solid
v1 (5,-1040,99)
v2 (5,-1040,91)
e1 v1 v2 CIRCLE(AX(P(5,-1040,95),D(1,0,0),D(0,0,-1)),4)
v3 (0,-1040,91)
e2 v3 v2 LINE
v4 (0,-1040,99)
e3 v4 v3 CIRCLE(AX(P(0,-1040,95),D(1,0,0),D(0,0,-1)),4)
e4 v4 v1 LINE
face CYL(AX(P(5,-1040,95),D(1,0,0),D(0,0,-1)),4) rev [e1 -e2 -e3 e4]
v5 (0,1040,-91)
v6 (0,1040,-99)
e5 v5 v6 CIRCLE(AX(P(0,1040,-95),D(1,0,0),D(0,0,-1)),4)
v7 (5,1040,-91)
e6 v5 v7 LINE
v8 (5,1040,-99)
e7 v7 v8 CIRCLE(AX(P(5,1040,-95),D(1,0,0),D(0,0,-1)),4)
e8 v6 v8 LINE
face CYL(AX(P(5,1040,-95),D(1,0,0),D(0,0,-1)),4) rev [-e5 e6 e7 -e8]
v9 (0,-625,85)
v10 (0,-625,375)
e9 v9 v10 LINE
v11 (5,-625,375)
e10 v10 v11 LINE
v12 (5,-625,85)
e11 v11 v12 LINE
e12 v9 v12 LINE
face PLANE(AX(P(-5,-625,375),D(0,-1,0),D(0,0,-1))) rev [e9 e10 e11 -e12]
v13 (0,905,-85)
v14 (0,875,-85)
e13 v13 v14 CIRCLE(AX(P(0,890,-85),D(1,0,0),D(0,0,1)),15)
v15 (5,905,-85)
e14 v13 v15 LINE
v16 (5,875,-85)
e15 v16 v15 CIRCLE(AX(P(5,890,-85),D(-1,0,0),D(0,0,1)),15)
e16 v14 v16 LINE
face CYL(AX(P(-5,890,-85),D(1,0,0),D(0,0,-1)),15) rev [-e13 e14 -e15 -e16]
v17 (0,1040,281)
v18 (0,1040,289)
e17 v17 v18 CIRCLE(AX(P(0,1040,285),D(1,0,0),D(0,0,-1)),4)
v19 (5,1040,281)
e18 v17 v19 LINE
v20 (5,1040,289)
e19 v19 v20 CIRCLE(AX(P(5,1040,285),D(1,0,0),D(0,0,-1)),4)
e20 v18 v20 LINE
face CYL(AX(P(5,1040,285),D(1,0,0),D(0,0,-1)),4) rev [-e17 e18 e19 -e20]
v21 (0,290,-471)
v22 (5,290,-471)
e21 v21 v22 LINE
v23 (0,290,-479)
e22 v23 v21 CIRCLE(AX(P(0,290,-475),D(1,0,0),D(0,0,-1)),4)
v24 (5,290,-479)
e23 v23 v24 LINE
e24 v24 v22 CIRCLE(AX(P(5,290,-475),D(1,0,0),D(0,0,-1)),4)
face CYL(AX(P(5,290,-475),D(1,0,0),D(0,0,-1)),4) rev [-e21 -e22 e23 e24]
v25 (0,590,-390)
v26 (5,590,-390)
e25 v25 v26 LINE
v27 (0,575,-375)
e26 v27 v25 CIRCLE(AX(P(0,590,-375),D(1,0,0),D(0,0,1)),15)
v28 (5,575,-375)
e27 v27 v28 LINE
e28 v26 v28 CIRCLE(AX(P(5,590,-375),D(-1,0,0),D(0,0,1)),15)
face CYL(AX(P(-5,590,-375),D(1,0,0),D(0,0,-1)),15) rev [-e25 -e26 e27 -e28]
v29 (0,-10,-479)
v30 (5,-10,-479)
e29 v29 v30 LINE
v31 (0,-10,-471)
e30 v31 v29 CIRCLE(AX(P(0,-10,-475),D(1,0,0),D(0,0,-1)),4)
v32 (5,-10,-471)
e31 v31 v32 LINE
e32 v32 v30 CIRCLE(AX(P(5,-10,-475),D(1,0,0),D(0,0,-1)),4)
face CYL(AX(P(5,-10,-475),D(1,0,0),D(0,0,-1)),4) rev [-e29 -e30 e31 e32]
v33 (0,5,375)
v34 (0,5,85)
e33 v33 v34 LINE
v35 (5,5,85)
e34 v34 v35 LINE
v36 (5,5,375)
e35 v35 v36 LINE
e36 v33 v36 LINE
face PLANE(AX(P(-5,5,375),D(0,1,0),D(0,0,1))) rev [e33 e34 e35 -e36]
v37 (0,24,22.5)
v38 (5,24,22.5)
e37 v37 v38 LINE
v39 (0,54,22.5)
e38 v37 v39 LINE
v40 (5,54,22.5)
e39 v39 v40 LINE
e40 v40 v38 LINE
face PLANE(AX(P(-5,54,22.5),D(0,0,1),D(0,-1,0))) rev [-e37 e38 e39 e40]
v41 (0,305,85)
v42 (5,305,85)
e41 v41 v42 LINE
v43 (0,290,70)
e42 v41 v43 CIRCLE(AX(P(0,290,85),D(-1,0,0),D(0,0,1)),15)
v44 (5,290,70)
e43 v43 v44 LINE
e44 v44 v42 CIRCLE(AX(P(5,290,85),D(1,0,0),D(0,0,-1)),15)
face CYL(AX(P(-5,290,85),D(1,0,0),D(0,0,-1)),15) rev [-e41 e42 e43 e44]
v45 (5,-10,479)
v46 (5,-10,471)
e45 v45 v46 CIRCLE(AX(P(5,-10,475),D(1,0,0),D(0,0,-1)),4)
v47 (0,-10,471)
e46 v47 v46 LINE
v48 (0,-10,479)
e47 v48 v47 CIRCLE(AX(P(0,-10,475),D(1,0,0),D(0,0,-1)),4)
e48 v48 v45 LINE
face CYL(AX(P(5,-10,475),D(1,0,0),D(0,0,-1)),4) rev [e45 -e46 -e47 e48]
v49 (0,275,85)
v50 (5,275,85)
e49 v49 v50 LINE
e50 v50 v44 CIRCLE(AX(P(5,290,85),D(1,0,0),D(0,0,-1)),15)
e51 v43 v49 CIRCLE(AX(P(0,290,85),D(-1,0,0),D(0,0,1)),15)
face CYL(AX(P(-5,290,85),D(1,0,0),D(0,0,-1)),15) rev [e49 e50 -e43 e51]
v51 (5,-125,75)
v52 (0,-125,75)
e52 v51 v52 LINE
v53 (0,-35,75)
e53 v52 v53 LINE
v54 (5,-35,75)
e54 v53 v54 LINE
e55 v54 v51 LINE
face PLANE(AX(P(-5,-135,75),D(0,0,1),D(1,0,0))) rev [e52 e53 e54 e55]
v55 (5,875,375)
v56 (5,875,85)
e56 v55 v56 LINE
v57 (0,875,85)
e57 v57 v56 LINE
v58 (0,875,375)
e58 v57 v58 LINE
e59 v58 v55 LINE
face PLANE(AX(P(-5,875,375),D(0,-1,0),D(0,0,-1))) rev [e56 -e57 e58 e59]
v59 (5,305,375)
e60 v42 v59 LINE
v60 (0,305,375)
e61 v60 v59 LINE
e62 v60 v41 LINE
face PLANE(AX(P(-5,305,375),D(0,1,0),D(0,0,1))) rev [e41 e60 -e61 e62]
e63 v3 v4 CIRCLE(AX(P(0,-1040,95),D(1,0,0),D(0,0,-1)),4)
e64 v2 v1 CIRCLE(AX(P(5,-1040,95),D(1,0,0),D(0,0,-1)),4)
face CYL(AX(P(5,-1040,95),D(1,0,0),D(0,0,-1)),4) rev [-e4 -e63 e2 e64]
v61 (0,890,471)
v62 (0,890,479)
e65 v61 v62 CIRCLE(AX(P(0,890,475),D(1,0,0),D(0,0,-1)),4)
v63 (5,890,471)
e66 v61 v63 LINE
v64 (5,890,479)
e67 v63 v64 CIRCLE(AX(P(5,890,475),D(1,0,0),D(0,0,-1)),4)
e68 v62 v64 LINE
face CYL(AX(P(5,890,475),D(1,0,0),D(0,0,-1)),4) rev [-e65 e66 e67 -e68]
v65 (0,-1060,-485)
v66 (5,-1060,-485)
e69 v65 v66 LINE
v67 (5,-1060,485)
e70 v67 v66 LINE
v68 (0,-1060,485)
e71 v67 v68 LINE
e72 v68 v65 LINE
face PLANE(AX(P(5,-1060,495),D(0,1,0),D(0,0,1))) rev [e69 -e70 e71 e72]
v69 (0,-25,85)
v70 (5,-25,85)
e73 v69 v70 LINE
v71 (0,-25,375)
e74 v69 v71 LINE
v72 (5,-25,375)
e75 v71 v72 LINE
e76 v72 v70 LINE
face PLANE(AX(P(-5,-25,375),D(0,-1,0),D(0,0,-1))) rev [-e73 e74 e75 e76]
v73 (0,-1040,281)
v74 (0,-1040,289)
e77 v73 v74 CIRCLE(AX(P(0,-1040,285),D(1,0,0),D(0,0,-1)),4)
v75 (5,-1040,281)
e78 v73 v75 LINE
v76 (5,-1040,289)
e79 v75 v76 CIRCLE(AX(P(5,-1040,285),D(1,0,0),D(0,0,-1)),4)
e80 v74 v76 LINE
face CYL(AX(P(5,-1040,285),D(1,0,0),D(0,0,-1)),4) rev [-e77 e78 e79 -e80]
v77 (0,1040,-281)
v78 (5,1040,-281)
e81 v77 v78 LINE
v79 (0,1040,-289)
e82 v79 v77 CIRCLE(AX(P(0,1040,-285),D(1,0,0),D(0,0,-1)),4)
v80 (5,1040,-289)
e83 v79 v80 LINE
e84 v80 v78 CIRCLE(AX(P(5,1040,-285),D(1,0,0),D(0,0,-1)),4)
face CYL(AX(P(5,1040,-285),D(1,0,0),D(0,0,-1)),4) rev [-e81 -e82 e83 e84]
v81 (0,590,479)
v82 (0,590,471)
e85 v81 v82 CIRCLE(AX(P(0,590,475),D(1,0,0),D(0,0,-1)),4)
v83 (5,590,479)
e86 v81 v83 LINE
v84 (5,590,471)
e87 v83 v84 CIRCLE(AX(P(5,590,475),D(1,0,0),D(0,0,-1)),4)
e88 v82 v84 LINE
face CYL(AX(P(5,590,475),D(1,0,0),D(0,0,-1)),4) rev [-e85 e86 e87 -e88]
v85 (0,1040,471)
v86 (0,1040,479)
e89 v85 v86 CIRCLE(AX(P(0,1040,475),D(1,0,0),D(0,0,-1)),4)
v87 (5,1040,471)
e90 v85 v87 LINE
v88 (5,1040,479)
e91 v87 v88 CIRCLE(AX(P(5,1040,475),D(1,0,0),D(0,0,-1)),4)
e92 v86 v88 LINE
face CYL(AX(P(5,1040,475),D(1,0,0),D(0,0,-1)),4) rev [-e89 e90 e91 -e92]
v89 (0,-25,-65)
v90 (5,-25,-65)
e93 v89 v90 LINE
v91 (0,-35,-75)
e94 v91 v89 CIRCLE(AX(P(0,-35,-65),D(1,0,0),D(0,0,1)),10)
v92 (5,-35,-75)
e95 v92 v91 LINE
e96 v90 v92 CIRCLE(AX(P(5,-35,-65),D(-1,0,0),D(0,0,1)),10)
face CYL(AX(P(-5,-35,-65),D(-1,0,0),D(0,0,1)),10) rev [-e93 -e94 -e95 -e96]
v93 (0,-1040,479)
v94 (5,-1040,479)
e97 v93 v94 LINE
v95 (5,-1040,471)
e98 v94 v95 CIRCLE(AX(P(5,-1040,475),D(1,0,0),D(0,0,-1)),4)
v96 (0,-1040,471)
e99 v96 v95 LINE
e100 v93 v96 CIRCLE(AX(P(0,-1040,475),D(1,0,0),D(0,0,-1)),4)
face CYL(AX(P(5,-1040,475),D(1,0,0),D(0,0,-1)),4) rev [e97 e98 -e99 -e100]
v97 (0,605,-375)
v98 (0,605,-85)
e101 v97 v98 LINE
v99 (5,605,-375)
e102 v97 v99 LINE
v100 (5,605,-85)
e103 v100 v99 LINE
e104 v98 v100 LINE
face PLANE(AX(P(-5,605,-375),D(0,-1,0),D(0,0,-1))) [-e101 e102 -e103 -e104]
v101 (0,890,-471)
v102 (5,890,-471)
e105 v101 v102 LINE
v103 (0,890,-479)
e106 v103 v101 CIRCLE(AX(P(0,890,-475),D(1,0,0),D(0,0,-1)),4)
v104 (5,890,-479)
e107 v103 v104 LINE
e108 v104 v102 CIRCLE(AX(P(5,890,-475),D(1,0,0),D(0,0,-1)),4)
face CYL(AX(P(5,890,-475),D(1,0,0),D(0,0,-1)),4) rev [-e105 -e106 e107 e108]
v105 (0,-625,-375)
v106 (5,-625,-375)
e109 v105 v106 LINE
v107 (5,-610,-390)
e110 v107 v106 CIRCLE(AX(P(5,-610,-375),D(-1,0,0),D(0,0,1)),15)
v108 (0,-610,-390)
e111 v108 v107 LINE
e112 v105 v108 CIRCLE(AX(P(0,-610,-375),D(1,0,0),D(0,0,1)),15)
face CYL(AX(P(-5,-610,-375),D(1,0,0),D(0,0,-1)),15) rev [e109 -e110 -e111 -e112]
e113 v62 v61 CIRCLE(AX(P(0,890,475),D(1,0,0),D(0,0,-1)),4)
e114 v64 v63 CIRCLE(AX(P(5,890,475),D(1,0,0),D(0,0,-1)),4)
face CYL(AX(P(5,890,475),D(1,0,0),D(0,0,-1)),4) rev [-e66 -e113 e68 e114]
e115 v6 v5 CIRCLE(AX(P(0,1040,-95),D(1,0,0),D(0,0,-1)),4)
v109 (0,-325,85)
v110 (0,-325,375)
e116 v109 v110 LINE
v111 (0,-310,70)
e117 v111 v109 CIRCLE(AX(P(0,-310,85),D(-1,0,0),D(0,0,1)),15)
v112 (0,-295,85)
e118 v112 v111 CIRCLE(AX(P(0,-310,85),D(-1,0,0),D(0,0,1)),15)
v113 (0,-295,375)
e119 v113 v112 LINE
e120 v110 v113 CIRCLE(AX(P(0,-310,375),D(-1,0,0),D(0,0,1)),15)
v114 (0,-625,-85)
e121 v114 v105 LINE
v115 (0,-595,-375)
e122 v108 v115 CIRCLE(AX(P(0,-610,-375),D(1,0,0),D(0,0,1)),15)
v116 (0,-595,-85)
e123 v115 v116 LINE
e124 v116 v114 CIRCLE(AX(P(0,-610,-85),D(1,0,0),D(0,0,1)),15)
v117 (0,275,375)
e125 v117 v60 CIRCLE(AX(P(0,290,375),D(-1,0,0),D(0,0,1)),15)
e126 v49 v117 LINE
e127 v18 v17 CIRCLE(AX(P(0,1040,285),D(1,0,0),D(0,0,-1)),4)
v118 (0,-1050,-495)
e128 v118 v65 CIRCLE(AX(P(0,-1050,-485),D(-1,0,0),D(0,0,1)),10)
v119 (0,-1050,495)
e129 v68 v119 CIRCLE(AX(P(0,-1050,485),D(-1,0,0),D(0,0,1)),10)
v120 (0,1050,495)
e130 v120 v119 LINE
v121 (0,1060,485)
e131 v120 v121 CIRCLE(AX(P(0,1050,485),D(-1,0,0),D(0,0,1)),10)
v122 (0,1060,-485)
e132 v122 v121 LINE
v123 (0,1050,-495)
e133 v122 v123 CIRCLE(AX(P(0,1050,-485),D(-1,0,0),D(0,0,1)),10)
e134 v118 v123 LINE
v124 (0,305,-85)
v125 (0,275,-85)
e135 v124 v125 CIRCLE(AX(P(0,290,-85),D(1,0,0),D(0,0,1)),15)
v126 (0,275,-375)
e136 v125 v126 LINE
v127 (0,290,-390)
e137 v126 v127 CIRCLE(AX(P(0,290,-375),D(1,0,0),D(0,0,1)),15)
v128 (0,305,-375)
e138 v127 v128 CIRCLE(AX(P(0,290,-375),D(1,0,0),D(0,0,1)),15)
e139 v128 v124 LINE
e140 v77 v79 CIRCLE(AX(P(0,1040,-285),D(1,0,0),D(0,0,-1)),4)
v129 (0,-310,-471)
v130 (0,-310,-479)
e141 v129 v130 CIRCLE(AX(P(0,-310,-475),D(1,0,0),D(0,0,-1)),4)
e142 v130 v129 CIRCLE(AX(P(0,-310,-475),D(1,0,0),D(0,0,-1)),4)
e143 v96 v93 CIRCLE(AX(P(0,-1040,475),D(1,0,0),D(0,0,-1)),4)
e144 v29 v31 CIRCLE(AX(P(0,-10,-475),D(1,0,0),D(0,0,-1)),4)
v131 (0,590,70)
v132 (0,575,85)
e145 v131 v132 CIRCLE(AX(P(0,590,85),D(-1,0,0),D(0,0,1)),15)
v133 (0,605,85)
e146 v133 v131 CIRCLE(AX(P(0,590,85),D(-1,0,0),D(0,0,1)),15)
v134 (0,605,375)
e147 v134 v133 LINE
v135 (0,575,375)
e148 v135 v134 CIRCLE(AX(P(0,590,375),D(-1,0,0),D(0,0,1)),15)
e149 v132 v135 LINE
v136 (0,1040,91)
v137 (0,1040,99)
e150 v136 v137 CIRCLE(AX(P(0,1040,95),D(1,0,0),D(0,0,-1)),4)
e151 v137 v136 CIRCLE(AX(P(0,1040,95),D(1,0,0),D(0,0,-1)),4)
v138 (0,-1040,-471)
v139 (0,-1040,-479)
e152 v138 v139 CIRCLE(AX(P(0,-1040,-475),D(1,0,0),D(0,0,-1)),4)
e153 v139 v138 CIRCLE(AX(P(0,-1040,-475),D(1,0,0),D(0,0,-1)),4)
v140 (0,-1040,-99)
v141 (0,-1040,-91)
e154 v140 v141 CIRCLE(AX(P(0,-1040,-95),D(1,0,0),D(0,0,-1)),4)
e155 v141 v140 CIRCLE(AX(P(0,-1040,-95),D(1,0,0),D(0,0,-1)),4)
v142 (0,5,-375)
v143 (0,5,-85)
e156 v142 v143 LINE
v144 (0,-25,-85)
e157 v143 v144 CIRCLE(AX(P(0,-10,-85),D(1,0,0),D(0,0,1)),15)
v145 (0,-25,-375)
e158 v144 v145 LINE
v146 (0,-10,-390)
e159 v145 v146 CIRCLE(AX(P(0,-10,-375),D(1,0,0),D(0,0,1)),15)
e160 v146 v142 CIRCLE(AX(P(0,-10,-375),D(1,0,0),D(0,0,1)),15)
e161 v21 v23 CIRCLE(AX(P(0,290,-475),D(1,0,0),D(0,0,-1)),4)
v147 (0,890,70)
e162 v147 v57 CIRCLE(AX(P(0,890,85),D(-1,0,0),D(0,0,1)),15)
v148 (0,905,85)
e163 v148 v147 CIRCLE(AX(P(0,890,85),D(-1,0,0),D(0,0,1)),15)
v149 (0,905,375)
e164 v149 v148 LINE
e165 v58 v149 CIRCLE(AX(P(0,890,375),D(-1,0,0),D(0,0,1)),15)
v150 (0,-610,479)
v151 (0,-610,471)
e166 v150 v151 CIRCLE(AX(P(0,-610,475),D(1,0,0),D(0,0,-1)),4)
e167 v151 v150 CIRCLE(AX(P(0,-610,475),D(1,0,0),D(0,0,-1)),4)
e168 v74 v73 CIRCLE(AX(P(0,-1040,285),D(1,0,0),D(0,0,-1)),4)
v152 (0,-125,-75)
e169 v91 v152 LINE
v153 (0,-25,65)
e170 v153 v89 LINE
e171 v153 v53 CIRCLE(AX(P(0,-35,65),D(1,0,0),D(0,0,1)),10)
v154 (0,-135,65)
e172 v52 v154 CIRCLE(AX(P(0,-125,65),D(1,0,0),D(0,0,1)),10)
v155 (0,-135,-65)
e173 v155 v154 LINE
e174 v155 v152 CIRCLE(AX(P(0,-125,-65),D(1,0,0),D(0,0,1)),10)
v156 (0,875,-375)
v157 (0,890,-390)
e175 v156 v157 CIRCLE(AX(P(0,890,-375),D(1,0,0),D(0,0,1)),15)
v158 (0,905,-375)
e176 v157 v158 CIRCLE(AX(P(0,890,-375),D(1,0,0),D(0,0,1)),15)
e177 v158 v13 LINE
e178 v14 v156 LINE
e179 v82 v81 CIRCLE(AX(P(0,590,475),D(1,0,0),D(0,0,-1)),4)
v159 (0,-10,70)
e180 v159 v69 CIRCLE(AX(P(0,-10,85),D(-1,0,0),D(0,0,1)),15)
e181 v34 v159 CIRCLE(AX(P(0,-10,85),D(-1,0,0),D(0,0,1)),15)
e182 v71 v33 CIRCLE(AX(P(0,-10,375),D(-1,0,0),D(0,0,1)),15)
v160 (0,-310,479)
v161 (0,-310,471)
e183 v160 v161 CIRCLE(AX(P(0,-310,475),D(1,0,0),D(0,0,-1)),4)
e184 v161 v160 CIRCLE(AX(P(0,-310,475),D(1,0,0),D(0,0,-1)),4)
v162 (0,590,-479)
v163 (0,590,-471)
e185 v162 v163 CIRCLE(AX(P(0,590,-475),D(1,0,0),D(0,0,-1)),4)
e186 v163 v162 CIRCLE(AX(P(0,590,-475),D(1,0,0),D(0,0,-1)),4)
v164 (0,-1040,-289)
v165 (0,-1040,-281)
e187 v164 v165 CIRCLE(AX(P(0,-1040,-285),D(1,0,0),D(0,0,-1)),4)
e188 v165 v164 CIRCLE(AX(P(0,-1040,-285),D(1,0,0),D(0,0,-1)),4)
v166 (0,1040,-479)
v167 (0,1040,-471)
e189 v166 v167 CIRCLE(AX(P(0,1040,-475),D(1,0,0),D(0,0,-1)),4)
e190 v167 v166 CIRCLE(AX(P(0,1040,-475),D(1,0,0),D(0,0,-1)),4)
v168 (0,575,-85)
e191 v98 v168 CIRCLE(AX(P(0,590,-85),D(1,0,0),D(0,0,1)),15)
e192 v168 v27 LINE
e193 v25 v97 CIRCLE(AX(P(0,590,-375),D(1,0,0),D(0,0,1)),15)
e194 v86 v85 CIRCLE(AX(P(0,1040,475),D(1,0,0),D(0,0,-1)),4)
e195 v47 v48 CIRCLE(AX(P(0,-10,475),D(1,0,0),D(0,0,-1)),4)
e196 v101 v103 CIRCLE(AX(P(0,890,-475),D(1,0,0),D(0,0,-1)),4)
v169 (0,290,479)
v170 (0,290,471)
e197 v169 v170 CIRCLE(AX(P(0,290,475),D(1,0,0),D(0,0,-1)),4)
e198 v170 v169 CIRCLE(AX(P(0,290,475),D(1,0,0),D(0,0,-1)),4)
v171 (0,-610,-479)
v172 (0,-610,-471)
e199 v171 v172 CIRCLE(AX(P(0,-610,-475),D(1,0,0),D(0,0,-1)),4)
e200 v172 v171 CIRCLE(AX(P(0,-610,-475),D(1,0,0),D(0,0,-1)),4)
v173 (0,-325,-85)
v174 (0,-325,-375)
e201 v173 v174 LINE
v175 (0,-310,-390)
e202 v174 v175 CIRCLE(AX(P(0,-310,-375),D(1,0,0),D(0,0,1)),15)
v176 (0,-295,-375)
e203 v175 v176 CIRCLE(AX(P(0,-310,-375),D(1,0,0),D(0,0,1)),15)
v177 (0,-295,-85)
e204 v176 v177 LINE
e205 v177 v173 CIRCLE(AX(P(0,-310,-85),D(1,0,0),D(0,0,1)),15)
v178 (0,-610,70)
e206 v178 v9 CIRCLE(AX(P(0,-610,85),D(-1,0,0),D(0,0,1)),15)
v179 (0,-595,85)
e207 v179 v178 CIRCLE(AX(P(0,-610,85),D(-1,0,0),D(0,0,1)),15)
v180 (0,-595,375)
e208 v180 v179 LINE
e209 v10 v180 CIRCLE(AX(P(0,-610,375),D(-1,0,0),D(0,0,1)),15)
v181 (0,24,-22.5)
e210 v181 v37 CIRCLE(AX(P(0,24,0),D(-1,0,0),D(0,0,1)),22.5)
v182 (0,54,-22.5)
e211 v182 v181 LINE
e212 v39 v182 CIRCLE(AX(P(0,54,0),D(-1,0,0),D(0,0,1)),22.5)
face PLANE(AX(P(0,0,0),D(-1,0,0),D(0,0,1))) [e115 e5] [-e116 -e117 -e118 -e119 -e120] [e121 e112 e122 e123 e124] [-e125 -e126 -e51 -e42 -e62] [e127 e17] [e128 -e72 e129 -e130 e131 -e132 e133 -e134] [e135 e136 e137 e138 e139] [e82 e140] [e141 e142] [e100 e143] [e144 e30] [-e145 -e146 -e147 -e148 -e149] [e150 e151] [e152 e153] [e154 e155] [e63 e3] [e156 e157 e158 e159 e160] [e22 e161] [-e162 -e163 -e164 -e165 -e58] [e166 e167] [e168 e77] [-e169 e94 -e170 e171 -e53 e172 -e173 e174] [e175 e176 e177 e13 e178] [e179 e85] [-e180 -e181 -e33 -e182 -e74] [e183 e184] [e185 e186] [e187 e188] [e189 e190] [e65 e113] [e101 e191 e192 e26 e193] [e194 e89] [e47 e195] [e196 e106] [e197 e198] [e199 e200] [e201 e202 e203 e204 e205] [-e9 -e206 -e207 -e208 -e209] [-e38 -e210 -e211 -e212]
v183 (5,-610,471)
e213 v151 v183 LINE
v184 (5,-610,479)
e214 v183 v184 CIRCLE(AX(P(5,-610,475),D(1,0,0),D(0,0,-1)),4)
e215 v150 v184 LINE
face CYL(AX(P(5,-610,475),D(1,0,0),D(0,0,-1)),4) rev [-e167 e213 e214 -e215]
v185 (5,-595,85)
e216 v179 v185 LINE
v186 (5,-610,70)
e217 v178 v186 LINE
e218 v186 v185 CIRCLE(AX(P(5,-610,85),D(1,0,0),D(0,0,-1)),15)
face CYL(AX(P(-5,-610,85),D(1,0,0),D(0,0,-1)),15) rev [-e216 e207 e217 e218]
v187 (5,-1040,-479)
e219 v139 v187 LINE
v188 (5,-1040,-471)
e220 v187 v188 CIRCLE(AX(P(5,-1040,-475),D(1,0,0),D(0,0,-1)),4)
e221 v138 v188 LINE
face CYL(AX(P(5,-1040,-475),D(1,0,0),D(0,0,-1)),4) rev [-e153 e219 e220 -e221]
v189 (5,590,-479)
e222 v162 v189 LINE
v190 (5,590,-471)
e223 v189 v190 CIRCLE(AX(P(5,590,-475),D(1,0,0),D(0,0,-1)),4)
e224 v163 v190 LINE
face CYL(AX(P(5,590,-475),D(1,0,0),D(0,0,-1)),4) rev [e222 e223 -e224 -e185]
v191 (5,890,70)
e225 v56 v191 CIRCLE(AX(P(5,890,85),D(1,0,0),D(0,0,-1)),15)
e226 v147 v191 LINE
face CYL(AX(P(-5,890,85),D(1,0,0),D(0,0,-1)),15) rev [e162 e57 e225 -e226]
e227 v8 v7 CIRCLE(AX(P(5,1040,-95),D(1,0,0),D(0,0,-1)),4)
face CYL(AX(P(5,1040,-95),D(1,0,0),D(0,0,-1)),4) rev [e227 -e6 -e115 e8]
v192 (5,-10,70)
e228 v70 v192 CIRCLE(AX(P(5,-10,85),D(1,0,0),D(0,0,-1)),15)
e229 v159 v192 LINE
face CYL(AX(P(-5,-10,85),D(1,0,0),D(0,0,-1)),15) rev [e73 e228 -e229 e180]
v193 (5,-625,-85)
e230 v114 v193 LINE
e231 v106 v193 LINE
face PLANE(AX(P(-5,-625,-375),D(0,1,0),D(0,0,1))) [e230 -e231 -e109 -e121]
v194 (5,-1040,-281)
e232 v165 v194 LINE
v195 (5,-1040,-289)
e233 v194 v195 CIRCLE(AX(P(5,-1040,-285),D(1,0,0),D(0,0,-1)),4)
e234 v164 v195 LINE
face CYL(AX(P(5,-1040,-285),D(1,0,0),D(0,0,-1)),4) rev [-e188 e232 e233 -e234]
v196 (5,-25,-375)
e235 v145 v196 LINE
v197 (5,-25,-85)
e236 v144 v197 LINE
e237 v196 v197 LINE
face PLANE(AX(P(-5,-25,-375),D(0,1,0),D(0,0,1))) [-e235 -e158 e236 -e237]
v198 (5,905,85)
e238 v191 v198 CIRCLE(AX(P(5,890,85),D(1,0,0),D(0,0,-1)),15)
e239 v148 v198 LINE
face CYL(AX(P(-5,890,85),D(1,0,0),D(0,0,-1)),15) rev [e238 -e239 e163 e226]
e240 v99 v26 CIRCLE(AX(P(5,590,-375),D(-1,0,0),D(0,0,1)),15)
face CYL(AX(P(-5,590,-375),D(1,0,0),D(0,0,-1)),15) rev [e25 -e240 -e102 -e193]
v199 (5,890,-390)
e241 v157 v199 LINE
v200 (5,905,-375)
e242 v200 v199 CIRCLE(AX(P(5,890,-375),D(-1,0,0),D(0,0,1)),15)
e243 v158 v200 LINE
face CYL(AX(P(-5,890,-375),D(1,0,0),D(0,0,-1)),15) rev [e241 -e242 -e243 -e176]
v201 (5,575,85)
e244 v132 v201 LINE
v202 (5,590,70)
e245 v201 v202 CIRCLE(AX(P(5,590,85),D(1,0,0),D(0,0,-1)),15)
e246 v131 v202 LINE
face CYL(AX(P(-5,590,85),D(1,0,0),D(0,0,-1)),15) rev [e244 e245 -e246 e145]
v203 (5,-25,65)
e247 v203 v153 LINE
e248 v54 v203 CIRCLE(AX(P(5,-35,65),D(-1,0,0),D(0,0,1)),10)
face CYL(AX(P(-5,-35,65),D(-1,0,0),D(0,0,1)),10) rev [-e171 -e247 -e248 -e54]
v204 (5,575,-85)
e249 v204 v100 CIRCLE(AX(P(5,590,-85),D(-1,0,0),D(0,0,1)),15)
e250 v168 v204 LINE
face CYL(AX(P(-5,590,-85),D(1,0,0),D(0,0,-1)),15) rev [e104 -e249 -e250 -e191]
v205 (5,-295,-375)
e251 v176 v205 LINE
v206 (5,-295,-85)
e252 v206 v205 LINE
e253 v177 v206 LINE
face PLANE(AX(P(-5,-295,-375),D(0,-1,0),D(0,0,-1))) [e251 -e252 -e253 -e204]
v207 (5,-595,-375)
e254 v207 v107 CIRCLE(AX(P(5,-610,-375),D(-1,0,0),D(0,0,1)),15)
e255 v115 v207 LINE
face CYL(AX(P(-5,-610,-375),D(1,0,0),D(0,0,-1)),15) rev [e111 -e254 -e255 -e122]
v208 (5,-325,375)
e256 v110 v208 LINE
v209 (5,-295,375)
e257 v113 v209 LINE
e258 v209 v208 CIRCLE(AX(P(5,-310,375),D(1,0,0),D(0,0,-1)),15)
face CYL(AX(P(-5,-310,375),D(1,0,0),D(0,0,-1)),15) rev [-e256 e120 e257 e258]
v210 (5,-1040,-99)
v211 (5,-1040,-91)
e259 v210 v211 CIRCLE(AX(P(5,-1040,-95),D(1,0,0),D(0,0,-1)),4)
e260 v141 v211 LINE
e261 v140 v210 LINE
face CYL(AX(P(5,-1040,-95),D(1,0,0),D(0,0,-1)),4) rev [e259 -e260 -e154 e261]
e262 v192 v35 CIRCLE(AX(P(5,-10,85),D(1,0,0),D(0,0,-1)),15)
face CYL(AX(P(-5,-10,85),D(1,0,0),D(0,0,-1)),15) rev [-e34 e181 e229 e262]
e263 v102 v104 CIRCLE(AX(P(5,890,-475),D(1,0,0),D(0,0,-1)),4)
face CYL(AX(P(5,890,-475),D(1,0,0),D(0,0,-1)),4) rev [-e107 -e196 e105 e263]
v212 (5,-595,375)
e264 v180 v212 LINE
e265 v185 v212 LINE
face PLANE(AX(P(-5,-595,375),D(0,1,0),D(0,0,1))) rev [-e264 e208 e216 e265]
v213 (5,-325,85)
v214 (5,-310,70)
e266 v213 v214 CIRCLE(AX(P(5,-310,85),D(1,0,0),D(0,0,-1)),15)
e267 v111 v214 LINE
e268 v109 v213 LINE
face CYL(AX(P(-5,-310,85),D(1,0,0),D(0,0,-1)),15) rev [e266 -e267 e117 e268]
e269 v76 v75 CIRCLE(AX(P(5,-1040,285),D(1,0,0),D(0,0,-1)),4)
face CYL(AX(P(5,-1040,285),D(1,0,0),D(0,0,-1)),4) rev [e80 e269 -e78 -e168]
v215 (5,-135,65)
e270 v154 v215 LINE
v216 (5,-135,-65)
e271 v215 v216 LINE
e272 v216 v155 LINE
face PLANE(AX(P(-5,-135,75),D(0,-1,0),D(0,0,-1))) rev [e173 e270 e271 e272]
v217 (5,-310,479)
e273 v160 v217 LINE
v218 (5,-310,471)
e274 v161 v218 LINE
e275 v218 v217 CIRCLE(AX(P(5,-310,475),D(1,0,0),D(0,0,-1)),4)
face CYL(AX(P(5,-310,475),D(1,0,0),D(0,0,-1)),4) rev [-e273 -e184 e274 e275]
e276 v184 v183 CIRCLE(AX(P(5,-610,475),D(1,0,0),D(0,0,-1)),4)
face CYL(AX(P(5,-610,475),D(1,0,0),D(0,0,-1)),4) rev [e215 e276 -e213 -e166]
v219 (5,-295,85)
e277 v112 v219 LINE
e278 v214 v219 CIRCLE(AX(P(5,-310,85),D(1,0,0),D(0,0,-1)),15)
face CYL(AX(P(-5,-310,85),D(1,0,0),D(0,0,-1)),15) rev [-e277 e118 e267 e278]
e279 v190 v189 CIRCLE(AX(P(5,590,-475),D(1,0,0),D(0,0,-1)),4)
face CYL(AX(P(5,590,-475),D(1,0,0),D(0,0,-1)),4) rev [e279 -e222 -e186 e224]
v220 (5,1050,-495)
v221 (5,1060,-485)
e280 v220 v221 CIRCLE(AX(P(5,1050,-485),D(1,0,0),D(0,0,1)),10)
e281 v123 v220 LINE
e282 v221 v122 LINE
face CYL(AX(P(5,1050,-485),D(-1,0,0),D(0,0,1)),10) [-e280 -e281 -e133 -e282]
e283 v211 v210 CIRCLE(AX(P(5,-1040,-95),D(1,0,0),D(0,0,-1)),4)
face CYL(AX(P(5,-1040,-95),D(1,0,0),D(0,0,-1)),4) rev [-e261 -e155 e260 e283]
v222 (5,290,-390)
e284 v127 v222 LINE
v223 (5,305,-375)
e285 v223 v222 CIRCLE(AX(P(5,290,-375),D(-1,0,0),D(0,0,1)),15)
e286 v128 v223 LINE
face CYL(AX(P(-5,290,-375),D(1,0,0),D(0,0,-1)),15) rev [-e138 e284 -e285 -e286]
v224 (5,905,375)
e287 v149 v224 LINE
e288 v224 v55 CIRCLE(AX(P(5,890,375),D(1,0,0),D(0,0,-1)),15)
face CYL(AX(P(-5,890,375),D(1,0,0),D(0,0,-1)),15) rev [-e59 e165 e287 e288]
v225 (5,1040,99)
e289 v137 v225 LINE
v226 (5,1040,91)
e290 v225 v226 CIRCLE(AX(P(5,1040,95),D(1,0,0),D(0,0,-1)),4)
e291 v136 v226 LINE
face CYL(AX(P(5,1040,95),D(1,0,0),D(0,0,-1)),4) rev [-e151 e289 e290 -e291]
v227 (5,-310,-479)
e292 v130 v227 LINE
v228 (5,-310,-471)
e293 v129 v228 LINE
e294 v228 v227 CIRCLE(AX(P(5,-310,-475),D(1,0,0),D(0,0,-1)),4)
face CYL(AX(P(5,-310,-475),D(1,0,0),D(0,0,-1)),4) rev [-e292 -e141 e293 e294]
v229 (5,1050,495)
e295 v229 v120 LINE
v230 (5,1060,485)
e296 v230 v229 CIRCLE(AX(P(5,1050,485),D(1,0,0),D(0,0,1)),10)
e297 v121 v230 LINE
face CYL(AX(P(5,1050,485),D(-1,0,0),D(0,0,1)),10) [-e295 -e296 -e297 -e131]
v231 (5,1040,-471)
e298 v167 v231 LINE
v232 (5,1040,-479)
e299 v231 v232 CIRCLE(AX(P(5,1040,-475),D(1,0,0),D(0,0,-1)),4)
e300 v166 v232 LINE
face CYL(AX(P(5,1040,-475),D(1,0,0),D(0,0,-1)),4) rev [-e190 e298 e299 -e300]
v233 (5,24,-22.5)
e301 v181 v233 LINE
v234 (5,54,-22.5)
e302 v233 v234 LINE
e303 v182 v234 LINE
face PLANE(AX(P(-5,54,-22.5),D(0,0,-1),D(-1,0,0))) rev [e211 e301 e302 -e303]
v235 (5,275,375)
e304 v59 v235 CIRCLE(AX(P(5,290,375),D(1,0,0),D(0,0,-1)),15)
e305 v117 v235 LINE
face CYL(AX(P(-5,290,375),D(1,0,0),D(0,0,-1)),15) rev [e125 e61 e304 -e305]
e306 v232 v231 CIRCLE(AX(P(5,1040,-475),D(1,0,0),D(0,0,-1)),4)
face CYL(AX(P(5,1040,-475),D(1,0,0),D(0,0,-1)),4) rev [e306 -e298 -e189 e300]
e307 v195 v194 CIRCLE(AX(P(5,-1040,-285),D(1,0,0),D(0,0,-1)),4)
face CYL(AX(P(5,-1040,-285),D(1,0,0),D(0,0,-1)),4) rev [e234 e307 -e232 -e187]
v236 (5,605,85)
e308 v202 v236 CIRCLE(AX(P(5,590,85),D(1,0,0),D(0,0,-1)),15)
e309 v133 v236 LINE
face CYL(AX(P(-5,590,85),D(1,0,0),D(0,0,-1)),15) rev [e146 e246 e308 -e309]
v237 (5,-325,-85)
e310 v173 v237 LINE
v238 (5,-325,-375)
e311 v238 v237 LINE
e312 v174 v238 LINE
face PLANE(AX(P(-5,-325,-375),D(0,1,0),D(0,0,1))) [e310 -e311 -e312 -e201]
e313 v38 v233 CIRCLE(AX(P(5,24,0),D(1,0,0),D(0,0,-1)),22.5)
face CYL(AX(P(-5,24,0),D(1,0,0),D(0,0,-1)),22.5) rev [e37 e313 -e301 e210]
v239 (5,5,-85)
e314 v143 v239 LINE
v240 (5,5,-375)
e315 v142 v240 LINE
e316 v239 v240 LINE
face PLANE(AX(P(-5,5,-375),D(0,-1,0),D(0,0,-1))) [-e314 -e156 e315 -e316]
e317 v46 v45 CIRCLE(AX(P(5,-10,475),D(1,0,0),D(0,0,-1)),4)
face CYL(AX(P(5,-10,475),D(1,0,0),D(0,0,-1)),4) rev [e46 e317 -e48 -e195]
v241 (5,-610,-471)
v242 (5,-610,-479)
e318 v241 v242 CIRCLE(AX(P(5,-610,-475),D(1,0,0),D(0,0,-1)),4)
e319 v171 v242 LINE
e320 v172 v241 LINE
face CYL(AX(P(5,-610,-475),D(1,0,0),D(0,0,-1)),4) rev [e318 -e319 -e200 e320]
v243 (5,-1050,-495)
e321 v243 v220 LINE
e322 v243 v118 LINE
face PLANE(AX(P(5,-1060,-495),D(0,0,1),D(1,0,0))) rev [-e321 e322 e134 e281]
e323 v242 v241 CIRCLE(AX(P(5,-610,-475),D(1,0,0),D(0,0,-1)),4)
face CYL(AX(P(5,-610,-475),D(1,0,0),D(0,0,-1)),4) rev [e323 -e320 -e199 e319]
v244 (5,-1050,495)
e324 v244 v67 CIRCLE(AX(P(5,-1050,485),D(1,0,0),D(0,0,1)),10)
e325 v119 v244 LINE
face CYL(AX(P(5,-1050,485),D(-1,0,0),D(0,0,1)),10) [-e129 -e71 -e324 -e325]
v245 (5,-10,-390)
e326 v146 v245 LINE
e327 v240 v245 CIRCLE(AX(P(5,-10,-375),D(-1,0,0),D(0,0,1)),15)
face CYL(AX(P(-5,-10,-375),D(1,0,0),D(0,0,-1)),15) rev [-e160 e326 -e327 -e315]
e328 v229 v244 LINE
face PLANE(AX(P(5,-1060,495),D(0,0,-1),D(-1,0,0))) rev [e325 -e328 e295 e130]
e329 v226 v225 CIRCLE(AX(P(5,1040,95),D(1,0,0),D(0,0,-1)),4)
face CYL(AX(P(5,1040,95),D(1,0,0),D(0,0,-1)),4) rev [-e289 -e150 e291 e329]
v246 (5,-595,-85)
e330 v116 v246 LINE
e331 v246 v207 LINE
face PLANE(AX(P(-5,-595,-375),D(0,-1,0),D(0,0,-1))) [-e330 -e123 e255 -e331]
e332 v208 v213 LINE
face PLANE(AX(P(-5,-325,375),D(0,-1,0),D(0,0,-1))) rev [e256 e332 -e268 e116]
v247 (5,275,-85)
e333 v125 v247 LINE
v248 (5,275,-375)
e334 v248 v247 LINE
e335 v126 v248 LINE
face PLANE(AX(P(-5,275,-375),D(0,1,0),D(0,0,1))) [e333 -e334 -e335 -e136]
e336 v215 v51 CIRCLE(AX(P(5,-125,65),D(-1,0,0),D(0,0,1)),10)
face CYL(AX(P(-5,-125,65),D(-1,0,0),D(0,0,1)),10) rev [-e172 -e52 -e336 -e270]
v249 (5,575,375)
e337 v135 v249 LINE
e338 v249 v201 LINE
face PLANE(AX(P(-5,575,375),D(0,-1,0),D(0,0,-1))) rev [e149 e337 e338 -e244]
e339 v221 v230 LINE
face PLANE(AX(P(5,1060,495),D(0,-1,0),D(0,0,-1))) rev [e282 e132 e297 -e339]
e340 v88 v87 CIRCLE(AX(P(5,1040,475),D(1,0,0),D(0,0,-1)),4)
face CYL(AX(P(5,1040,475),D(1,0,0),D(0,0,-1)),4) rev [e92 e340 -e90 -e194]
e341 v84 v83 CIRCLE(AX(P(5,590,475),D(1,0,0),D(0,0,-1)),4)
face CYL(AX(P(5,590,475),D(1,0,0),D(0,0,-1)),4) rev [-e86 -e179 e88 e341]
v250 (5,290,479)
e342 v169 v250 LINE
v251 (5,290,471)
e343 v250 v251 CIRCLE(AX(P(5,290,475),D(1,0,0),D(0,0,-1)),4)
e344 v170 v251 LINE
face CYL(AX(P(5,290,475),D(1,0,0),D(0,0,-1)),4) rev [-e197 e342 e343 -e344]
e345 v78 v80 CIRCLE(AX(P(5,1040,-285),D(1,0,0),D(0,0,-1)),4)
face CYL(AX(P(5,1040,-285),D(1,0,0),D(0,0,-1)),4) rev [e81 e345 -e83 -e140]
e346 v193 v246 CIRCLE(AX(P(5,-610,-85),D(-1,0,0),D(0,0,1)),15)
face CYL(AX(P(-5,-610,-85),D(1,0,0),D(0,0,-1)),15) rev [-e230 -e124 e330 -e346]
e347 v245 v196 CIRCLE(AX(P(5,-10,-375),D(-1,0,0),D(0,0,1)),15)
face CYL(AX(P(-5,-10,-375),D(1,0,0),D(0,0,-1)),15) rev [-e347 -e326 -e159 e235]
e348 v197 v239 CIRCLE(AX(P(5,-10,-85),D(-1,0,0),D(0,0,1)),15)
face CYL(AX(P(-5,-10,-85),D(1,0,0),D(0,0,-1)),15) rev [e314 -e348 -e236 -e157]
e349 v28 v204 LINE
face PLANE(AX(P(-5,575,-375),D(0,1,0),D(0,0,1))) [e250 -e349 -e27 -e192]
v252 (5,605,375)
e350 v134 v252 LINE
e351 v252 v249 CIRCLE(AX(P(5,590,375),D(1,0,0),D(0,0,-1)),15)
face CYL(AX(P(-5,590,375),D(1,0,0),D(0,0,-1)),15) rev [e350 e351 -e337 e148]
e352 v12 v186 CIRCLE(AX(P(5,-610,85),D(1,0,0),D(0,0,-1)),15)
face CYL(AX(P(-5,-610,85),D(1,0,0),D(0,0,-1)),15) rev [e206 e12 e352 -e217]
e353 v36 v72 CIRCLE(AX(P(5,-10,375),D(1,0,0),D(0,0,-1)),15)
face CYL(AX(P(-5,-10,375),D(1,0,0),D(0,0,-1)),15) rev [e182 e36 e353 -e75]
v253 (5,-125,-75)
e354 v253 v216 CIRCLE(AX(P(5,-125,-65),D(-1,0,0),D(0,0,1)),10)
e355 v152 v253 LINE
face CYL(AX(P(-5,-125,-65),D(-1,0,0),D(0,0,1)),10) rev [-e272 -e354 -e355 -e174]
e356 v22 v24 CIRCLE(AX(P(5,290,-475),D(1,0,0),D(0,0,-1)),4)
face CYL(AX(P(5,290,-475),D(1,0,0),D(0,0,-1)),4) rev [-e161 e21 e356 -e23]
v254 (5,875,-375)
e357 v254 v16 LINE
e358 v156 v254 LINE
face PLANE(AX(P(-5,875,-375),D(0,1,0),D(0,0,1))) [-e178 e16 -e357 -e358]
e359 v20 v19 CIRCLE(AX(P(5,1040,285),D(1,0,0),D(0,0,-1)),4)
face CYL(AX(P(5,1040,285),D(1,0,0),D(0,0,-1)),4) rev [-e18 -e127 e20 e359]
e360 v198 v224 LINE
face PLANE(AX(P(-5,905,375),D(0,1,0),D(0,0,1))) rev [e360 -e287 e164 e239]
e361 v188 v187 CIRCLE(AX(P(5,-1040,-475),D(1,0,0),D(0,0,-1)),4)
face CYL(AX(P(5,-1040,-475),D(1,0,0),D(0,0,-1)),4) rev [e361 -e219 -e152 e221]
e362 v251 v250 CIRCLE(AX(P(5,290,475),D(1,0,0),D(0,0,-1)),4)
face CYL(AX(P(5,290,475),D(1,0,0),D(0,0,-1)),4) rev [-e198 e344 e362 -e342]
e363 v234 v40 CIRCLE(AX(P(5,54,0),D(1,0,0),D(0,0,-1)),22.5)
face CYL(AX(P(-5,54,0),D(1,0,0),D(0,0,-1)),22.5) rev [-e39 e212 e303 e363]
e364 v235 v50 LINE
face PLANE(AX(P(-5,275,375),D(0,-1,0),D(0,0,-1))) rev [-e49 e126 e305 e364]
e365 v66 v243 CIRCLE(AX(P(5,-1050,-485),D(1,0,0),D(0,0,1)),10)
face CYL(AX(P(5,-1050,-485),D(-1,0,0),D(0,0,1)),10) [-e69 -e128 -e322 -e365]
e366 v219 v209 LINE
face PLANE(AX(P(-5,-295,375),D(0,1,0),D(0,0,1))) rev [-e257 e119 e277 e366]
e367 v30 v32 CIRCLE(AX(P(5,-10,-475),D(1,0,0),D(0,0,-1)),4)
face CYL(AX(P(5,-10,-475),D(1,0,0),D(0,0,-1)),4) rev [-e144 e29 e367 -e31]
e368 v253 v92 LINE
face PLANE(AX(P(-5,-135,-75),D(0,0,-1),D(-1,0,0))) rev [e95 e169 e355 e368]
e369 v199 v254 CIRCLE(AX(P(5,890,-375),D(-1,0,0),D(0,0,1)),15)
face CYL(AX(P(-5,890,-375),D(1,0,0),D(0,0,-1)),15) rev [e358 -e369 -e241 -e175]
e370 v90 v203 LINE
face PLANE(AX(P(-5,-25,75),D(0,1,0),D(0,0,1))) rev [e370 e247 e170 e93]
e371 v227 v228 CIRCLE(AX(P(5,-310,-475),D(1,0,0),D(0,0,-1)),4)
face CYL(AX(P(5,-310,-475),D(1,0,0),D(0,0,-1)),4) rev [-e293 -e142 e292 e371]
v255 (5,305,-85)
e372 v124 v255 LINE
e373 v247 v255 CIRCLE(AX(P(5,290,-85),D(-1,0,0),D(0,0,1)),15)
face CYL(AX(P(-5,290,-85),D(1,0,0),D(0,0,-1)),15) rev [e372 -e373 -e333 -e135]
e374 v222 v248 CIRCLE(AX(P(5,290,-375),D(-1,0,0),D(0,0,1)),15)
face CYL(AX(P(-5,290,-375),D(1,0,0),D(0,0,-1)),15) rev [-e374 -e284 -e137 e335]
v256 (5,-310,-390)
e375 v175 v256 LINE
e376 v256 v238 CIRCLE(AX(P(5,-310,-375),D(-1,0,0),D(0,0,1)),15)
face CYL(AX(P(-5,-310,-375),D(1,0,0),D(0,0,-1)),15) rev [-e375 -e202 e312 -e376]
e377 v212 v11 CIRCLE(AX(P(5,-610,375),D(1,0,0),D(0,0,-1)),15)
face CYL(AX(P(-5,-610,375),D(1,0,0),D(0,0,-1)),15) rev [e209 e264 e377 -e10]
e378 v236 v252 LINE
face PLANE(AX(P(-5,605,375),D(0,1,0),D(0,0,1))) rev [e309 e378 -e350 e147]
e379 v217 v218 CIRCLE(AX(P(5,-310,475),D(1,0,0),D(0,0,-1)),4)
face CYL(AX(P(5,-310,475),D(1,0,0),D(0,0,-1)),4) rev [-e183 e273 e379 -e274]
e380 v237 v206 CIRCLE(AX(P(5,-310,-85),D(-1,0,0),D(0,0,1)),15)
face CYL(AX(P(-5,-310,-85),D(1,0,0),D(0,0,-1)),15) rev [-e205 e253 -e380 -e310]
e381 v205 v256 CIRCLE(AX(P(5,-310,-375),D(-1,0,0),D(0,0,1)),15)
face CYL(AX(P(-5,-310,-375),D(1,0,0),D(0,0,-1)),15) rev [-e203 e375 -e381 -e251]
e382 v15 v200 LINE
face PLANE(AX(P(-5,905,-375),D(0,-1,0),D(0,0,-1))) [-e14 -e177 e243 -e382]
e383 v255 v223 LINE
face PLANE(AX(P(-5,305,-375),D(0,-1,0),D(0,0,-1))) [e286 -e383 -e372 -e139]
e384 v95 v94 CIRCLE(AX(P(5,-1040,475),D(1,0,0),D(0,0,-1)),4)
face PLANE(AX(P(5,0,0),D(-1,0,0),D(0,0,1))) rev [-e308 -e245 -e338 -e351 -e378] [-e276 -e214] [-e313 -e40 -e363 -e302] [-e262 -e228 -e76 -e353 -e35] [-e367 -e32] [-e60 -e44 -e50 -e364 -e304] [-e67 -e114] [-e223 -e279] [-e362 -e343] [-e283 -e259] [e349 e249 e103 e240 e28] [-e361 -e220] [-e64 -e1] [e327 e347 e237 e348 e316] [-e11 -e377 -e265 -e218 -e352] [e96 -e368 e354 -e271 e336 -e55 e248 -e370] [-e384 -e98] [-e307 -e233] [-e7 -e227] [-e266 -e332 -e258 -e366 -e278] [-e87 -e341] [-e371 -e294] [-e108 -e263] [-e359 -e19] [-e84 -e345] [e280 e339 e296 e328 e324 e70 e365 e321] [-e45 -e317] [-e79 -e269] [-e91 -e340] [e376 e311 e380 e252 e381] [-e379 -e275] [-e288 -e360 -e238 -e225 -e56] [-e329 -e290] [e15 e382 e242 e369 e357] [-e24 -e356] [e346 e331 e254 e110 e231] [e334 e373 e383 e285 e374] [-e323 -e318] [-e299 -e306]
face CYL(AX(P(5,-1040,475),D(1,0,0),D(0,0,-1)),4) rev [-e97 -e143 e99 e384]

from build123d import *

# Parameters (mm, degrees)
SKETCH1_W                     = 990
SKETCH1_H                     = 2120
BOSS_EXTRUDE1_DEPTH           = 5
FILLET1_R                     = 10
M7_CLEARANCE_HOLE3_D          = 8
M7_CLEARANCE_HOLE2_AT_2_COUNT = 2
M7_CLEARANCE_HOLE2_AT_2_PITCH = 950
LPATTERN7_COUNT               = 6
LPATTERN7_PITCH               = 300
SKETCH16_W                    = 150
SKETCH16_H                    = 110
CUT_EXTRUDE4_DEPTH            = 10
FILLET2_R                     = 10
CUT_EXTRUDE5_DEPTH            = 10
LPATTERN8_COUNT               = 6
LPATTERN8_PITCH               = 300
MIRROR6_COPY_1_DEPTH          = 10
MIRROR6_COPY_2_DEPTH          = 10
MIRROR6_COPY_3_DEPTH          = 10
MIRROR6_COPY_4_DEPTH          = 10
MIRROR6_COPY_5_DEPTH          = 10


with BuildPart() as part:
    # Sketch1 → Boss-Extrude1 (new body)
    with BuildSketch(Plane(origin=(0, 0, 0), x_dir=(0, 0, -1), z_dir=(1, 0, 0))):
        Rectangle(SKETCH1_W, SKETCH1_H)
    extrude(amount=BOSS_EXTRUDE1_DEPTH)

    # Fillet1
    fillet1_edges = [part.edges().sort_by_distance(p)[0] for p in [
        (2.5, -1060, -495),
        (2.5, -1060, 495),
        (2.5, 1060, 495),
        (2.5, 1060, -495),
    ]]
    fillet(fillet1_edges, radius=FILLET1_R)

    # M7 Clearance Hole3 (through all)
    with Locations(Plane(origin=(5, 0, 0), x_dir=(0, 0, -1), z_dir=(1, 0, 0))):
        with Locations((-475, 1040), (-285, 1040), (-95, 1040), (95, 1040), (285, 1040), (475, 1040)):
            m7_clearance_hole3 = Hole(M7_CLEARANCE_HOLE3_D / 2)

    # Mirror5: M7 Clearance Hole3 across plane
    add(m7_clearance_hole3.mirror(Plane(origin=(0, 0, 0), x_dir=(0, 0, 1), z_dir=(0, -1, 0))), mode=Mode.SUBTRACT)

    # Sketch15 → M7 Clearance Hole2 (revolve, cut)
    with BuildSketch(Plane(origin=(5, 890, 475), x_dir=(0, 0, -1), z_dir=(0, 1, 0))):
        Polygon((0, 0), (0, 7.403442476), (4, 5), (4, 0), align=None)
    m7_clearance_hole2 = revolve(axis=Axis((11.35, 890, 475), (-1, 0, 0)), mode=Mode.SUBTRACT)

    # M7 Clearance Hole2 at 2: M7 Clearance Hole2 ×2
    with Locations(*[(0, 0, -i * M7_CLEARANCE_HOLE2_AT_2_PITCH) for i in range(1, M7_CLEARANCE_HOLE2_AT_2_COUNT)]):
        add(m7_clearance_hole2, mode=Mode.SUBTRACT)

    # LPattern7: M7 Clearance Hole2 ×6
    with Locations(*[(0, -i * LPATTERN7_PITCH, 0) for i in range(1, LPATTERN7_COUNT)]):
        add(m7_clearance_hole2, mode=Mode.SUBTRACT)

    # LPattern7 copy 1 sketch → LPattern7 copy 1 (revolve, cut)
    with BuildSketch(Plane(origin=(5, 590, -475), x_dir=(0, 0, -1), z_dir=(0, 1, 0))):
        Polygon((0, 0), (0, 7.403442476), (4, 5), (4, 0), align=None)
    revolve(axis=Axis((11.35, 590, -475), (-1, 0, 0)), mode=Mode.SUBTRACT)

    # LPattern7 copy 2 sketch → LPattern7 copy 2 (revolve, cut)
    with BuildSketch(Plane(origin=(5, 290, -475), x_dir=(0, 0, -1), z_dir=(0, 1, 0))):
        Polygon((0, 0), (0, 7.403442476), (4, 5), (4, 0), align=None)
    revolve(axis=Axis((11.35, 290, -475), (-1, 0, 0)), mode=Mode.SUBTRACT)

    # LPattern7 copy 3 sketch → LPattern7 copy 3 (revolve, cut)
    with BuildSketch(Plane(origin=(5, -10, -475), x_dir=(0, 0, -1), z_dir=(0, 1, 0))):
        Polygon((0, 0), (0, 7.403442476), (4, 5), (4, 0), align=None)
    revolve(axis=Axis((11.35, -10, -475), (-1, 0, 0)), mode=Mode.SUBTRACT)

    # LPattern7 copy 4 sketch → LPattern7 copy 4 (revolve, cut)
    with BuildSketch(Plane(origin=(5, -310, -475), x_dir=(0, 0, -1), z_dir=(0, 1, 0))):
        Polygon((0, 0), (0, 7.403442476), (4, 5), (4, 0), align=None)
    revolve(axis=Axis((11.35, -310, -475), (-1, 0, 0)), mode=Mode.SUBTRACT)

    # LPattern7 copy 5 sketch → LPattern7 copy 5 (revolve, cut)
    with BuildSketch(Plane(origin=(5, -610, -475), x_dir=(0, 0, -1), z_dir=(0, 1, 0))):
        Polygon((0, 0), (0, 7.403442476), (4, 5), (4, 0), align=None)
    revolve(axis=Axis((11.35, -610, -475), (-1, 0, 0)), mode=Mode.SUBTRACT)

    # Sketch16 → Cut-Extrude4 (cut)
    with BuildSketch(Plane(origin=(5, 0, 0), x_dir=(0, 0, -1), z_dir=(1, 0, 0))):
        with BuildLine():
            Line((22.5, 54), (22.5, 24))
            ThreePointArc((22.5, 24), (0, 1.5), (-22.5, 24))
            Line((-22.5, 24), (-22.5, 54))
            ThreePointArc((-22.5, 54), (0, 76.5), (22.5, 54))
        make_face()
        with Locations((0, -80)):
            Rectangle(SKETCH16_W, SKETCH16_H)
    extrude(amount=-CUT_EXTRUDE4_DEPTH, mode=Mode.SUBTRACT)

    # Fillet2
    fillet2_edges = [part.edges().sort_by_distance(p)[0] for p in [
        (2.5, -25, -75),
        (2.5, -135, -75),
        (2.5, -135, 75),
        (2.5, -25, 75),
    ]]
    fillet(fillet2_edges, radius=FILLET2_R)

    # Sketch18 → Cut-Extrude5 (cut)
    with BuildSketch(Plane(origin=(5, 0, 0), x_dir=(0, 0, -1), z_dir=(1, 0, 0))):
        with BuildLine():
            Line((-375, 905), (-85, 905))
            ThreePointArc((-85, 905), (-70, 890), (-85, 875))
            Line((-85, 875), (-375, 875))
            ThreePointArc((-375, 875), (-390, 890), (-375, 905))
        make_face()
    cut_extrude5 = extrude(amount=-CUT_EXTRUDE5_DEPTH, mode=Mode.SUBTRACT)

    # LPattern8: Cut-Extrude5 ×6
    with Locations(*[(0, -i * LPATTERN8_PITCH, 0) for i in range(1, LPATTERN8_COUNT)]):
        add(cut_extrude5, mode=Mode.SUBTRACT)

    # Mirror6: Cut-Extrude5 across plane
    add(cut_extrude5.mirror(Plane.XY), mode=Mode.SUBTRACT)

    # Mirror6 copy 1 sketch → Mirror6 copy 1 (cut)
    with BuildSketch(Plane(origin=(5, -300, 0), x_dir=(0, 0, 1), z_dir=(1, 0, 0))):
        with BuildLine():
            Line((-375, -905), (-85, -905))
            ThreePointArc((-85, -905), (-70, -890), (-85, -875))
            Line((-85, -875), (-375, -875))
            ThreePointArc((-375, -875), (-390, -890), (-375, -905))
        make_face()
    extrude(amount=-MIRROR6_COPY_1_DEPTH, mode=Mode.SUBTRACT)

    # Mirror6 copy 2 sketch → Mirror6 copy 2 (cut)
    with BuildSketch(Plane(origin=(5, -600, 0), x_dir=(0, 0, 1), z_dir=(1, 0, 0))):
        with BuildLine():
            Line((-375, -905), (-85, -905))
            ThreePointArc((-85, -905), (-70, -890), (-85, -875))
            Line((-85, -875), (-375, -875))
            ThreePointArc((-375, -875), (-390, -890), (-375, -905))
        make_face()
    extrude(amount=-MIRROR6_COPY_2_DEPTH, mode=Mode.SUBTRACT)

    # Mirror6 copy 3 sketch → Mirror6 copy 3 (cut)
    with BuildSketch(Plane(origin=(5, -900, 0), x_dir=(0, 0, 1), z_dir=(1, 0, 0))):
        with BuildLine():
            Line((-375, -905), (-85, -905))
            ThreePointArc((-85, -905), (-70, -890), (-85, -875))
            Line((-85, -875), (-375, -875))
            ThreePointArc((-375, -875), (-390, -890), (-375, -905))
        make_face()
    extrude(amount=-MIRROR6_COPY_3_DEPTH, mode=Mode.SUBTRACT)

    # Mirror6 copy 4 sketch → Mirror6 copy 4 (cut)
    with BuildSketch(Plane(origin=(5, -1200, 0), x_dir=(0, 0, 1), z_dir=(1, 0, 0))):
        with BuildLine():
            Line((-375, -905), (-85, -905))
            ThreePointArc((-85, -905), (-70, -890), (-85, -875))
            Line((-85, -875), (-375, -875))
            ThreePointArc((-375, -875), (-390, -890), (-375, -905))
        make_face()
    extrude(amount=-MIRROR6_COPY_4_DEPTH, mode=Mode.SUBTRACT)

    # Mirror6 copy 5 sketch → Mirror6 copy 5 (cut)
    with BuildSketch(Plane(origin=(5, -1500, 0), x_dir=(0, 0, 1), z_dir=(1, 0, 0))):
        with BuildLine():
            Line((-375, -905), (-85, -905))
            ThreePointArc((-85, -905), (-70, -890), (-85, -875))
            Line((-85, -875), (-375, -875))
            ThreePointArc((-375, -875), (-390, -890), (-375, -905))
        make_face()
    extrude(amount=-MIRROR6_COPY_5_DEPTH, mode=Mode.SUBTRACT)


solid = part.part
